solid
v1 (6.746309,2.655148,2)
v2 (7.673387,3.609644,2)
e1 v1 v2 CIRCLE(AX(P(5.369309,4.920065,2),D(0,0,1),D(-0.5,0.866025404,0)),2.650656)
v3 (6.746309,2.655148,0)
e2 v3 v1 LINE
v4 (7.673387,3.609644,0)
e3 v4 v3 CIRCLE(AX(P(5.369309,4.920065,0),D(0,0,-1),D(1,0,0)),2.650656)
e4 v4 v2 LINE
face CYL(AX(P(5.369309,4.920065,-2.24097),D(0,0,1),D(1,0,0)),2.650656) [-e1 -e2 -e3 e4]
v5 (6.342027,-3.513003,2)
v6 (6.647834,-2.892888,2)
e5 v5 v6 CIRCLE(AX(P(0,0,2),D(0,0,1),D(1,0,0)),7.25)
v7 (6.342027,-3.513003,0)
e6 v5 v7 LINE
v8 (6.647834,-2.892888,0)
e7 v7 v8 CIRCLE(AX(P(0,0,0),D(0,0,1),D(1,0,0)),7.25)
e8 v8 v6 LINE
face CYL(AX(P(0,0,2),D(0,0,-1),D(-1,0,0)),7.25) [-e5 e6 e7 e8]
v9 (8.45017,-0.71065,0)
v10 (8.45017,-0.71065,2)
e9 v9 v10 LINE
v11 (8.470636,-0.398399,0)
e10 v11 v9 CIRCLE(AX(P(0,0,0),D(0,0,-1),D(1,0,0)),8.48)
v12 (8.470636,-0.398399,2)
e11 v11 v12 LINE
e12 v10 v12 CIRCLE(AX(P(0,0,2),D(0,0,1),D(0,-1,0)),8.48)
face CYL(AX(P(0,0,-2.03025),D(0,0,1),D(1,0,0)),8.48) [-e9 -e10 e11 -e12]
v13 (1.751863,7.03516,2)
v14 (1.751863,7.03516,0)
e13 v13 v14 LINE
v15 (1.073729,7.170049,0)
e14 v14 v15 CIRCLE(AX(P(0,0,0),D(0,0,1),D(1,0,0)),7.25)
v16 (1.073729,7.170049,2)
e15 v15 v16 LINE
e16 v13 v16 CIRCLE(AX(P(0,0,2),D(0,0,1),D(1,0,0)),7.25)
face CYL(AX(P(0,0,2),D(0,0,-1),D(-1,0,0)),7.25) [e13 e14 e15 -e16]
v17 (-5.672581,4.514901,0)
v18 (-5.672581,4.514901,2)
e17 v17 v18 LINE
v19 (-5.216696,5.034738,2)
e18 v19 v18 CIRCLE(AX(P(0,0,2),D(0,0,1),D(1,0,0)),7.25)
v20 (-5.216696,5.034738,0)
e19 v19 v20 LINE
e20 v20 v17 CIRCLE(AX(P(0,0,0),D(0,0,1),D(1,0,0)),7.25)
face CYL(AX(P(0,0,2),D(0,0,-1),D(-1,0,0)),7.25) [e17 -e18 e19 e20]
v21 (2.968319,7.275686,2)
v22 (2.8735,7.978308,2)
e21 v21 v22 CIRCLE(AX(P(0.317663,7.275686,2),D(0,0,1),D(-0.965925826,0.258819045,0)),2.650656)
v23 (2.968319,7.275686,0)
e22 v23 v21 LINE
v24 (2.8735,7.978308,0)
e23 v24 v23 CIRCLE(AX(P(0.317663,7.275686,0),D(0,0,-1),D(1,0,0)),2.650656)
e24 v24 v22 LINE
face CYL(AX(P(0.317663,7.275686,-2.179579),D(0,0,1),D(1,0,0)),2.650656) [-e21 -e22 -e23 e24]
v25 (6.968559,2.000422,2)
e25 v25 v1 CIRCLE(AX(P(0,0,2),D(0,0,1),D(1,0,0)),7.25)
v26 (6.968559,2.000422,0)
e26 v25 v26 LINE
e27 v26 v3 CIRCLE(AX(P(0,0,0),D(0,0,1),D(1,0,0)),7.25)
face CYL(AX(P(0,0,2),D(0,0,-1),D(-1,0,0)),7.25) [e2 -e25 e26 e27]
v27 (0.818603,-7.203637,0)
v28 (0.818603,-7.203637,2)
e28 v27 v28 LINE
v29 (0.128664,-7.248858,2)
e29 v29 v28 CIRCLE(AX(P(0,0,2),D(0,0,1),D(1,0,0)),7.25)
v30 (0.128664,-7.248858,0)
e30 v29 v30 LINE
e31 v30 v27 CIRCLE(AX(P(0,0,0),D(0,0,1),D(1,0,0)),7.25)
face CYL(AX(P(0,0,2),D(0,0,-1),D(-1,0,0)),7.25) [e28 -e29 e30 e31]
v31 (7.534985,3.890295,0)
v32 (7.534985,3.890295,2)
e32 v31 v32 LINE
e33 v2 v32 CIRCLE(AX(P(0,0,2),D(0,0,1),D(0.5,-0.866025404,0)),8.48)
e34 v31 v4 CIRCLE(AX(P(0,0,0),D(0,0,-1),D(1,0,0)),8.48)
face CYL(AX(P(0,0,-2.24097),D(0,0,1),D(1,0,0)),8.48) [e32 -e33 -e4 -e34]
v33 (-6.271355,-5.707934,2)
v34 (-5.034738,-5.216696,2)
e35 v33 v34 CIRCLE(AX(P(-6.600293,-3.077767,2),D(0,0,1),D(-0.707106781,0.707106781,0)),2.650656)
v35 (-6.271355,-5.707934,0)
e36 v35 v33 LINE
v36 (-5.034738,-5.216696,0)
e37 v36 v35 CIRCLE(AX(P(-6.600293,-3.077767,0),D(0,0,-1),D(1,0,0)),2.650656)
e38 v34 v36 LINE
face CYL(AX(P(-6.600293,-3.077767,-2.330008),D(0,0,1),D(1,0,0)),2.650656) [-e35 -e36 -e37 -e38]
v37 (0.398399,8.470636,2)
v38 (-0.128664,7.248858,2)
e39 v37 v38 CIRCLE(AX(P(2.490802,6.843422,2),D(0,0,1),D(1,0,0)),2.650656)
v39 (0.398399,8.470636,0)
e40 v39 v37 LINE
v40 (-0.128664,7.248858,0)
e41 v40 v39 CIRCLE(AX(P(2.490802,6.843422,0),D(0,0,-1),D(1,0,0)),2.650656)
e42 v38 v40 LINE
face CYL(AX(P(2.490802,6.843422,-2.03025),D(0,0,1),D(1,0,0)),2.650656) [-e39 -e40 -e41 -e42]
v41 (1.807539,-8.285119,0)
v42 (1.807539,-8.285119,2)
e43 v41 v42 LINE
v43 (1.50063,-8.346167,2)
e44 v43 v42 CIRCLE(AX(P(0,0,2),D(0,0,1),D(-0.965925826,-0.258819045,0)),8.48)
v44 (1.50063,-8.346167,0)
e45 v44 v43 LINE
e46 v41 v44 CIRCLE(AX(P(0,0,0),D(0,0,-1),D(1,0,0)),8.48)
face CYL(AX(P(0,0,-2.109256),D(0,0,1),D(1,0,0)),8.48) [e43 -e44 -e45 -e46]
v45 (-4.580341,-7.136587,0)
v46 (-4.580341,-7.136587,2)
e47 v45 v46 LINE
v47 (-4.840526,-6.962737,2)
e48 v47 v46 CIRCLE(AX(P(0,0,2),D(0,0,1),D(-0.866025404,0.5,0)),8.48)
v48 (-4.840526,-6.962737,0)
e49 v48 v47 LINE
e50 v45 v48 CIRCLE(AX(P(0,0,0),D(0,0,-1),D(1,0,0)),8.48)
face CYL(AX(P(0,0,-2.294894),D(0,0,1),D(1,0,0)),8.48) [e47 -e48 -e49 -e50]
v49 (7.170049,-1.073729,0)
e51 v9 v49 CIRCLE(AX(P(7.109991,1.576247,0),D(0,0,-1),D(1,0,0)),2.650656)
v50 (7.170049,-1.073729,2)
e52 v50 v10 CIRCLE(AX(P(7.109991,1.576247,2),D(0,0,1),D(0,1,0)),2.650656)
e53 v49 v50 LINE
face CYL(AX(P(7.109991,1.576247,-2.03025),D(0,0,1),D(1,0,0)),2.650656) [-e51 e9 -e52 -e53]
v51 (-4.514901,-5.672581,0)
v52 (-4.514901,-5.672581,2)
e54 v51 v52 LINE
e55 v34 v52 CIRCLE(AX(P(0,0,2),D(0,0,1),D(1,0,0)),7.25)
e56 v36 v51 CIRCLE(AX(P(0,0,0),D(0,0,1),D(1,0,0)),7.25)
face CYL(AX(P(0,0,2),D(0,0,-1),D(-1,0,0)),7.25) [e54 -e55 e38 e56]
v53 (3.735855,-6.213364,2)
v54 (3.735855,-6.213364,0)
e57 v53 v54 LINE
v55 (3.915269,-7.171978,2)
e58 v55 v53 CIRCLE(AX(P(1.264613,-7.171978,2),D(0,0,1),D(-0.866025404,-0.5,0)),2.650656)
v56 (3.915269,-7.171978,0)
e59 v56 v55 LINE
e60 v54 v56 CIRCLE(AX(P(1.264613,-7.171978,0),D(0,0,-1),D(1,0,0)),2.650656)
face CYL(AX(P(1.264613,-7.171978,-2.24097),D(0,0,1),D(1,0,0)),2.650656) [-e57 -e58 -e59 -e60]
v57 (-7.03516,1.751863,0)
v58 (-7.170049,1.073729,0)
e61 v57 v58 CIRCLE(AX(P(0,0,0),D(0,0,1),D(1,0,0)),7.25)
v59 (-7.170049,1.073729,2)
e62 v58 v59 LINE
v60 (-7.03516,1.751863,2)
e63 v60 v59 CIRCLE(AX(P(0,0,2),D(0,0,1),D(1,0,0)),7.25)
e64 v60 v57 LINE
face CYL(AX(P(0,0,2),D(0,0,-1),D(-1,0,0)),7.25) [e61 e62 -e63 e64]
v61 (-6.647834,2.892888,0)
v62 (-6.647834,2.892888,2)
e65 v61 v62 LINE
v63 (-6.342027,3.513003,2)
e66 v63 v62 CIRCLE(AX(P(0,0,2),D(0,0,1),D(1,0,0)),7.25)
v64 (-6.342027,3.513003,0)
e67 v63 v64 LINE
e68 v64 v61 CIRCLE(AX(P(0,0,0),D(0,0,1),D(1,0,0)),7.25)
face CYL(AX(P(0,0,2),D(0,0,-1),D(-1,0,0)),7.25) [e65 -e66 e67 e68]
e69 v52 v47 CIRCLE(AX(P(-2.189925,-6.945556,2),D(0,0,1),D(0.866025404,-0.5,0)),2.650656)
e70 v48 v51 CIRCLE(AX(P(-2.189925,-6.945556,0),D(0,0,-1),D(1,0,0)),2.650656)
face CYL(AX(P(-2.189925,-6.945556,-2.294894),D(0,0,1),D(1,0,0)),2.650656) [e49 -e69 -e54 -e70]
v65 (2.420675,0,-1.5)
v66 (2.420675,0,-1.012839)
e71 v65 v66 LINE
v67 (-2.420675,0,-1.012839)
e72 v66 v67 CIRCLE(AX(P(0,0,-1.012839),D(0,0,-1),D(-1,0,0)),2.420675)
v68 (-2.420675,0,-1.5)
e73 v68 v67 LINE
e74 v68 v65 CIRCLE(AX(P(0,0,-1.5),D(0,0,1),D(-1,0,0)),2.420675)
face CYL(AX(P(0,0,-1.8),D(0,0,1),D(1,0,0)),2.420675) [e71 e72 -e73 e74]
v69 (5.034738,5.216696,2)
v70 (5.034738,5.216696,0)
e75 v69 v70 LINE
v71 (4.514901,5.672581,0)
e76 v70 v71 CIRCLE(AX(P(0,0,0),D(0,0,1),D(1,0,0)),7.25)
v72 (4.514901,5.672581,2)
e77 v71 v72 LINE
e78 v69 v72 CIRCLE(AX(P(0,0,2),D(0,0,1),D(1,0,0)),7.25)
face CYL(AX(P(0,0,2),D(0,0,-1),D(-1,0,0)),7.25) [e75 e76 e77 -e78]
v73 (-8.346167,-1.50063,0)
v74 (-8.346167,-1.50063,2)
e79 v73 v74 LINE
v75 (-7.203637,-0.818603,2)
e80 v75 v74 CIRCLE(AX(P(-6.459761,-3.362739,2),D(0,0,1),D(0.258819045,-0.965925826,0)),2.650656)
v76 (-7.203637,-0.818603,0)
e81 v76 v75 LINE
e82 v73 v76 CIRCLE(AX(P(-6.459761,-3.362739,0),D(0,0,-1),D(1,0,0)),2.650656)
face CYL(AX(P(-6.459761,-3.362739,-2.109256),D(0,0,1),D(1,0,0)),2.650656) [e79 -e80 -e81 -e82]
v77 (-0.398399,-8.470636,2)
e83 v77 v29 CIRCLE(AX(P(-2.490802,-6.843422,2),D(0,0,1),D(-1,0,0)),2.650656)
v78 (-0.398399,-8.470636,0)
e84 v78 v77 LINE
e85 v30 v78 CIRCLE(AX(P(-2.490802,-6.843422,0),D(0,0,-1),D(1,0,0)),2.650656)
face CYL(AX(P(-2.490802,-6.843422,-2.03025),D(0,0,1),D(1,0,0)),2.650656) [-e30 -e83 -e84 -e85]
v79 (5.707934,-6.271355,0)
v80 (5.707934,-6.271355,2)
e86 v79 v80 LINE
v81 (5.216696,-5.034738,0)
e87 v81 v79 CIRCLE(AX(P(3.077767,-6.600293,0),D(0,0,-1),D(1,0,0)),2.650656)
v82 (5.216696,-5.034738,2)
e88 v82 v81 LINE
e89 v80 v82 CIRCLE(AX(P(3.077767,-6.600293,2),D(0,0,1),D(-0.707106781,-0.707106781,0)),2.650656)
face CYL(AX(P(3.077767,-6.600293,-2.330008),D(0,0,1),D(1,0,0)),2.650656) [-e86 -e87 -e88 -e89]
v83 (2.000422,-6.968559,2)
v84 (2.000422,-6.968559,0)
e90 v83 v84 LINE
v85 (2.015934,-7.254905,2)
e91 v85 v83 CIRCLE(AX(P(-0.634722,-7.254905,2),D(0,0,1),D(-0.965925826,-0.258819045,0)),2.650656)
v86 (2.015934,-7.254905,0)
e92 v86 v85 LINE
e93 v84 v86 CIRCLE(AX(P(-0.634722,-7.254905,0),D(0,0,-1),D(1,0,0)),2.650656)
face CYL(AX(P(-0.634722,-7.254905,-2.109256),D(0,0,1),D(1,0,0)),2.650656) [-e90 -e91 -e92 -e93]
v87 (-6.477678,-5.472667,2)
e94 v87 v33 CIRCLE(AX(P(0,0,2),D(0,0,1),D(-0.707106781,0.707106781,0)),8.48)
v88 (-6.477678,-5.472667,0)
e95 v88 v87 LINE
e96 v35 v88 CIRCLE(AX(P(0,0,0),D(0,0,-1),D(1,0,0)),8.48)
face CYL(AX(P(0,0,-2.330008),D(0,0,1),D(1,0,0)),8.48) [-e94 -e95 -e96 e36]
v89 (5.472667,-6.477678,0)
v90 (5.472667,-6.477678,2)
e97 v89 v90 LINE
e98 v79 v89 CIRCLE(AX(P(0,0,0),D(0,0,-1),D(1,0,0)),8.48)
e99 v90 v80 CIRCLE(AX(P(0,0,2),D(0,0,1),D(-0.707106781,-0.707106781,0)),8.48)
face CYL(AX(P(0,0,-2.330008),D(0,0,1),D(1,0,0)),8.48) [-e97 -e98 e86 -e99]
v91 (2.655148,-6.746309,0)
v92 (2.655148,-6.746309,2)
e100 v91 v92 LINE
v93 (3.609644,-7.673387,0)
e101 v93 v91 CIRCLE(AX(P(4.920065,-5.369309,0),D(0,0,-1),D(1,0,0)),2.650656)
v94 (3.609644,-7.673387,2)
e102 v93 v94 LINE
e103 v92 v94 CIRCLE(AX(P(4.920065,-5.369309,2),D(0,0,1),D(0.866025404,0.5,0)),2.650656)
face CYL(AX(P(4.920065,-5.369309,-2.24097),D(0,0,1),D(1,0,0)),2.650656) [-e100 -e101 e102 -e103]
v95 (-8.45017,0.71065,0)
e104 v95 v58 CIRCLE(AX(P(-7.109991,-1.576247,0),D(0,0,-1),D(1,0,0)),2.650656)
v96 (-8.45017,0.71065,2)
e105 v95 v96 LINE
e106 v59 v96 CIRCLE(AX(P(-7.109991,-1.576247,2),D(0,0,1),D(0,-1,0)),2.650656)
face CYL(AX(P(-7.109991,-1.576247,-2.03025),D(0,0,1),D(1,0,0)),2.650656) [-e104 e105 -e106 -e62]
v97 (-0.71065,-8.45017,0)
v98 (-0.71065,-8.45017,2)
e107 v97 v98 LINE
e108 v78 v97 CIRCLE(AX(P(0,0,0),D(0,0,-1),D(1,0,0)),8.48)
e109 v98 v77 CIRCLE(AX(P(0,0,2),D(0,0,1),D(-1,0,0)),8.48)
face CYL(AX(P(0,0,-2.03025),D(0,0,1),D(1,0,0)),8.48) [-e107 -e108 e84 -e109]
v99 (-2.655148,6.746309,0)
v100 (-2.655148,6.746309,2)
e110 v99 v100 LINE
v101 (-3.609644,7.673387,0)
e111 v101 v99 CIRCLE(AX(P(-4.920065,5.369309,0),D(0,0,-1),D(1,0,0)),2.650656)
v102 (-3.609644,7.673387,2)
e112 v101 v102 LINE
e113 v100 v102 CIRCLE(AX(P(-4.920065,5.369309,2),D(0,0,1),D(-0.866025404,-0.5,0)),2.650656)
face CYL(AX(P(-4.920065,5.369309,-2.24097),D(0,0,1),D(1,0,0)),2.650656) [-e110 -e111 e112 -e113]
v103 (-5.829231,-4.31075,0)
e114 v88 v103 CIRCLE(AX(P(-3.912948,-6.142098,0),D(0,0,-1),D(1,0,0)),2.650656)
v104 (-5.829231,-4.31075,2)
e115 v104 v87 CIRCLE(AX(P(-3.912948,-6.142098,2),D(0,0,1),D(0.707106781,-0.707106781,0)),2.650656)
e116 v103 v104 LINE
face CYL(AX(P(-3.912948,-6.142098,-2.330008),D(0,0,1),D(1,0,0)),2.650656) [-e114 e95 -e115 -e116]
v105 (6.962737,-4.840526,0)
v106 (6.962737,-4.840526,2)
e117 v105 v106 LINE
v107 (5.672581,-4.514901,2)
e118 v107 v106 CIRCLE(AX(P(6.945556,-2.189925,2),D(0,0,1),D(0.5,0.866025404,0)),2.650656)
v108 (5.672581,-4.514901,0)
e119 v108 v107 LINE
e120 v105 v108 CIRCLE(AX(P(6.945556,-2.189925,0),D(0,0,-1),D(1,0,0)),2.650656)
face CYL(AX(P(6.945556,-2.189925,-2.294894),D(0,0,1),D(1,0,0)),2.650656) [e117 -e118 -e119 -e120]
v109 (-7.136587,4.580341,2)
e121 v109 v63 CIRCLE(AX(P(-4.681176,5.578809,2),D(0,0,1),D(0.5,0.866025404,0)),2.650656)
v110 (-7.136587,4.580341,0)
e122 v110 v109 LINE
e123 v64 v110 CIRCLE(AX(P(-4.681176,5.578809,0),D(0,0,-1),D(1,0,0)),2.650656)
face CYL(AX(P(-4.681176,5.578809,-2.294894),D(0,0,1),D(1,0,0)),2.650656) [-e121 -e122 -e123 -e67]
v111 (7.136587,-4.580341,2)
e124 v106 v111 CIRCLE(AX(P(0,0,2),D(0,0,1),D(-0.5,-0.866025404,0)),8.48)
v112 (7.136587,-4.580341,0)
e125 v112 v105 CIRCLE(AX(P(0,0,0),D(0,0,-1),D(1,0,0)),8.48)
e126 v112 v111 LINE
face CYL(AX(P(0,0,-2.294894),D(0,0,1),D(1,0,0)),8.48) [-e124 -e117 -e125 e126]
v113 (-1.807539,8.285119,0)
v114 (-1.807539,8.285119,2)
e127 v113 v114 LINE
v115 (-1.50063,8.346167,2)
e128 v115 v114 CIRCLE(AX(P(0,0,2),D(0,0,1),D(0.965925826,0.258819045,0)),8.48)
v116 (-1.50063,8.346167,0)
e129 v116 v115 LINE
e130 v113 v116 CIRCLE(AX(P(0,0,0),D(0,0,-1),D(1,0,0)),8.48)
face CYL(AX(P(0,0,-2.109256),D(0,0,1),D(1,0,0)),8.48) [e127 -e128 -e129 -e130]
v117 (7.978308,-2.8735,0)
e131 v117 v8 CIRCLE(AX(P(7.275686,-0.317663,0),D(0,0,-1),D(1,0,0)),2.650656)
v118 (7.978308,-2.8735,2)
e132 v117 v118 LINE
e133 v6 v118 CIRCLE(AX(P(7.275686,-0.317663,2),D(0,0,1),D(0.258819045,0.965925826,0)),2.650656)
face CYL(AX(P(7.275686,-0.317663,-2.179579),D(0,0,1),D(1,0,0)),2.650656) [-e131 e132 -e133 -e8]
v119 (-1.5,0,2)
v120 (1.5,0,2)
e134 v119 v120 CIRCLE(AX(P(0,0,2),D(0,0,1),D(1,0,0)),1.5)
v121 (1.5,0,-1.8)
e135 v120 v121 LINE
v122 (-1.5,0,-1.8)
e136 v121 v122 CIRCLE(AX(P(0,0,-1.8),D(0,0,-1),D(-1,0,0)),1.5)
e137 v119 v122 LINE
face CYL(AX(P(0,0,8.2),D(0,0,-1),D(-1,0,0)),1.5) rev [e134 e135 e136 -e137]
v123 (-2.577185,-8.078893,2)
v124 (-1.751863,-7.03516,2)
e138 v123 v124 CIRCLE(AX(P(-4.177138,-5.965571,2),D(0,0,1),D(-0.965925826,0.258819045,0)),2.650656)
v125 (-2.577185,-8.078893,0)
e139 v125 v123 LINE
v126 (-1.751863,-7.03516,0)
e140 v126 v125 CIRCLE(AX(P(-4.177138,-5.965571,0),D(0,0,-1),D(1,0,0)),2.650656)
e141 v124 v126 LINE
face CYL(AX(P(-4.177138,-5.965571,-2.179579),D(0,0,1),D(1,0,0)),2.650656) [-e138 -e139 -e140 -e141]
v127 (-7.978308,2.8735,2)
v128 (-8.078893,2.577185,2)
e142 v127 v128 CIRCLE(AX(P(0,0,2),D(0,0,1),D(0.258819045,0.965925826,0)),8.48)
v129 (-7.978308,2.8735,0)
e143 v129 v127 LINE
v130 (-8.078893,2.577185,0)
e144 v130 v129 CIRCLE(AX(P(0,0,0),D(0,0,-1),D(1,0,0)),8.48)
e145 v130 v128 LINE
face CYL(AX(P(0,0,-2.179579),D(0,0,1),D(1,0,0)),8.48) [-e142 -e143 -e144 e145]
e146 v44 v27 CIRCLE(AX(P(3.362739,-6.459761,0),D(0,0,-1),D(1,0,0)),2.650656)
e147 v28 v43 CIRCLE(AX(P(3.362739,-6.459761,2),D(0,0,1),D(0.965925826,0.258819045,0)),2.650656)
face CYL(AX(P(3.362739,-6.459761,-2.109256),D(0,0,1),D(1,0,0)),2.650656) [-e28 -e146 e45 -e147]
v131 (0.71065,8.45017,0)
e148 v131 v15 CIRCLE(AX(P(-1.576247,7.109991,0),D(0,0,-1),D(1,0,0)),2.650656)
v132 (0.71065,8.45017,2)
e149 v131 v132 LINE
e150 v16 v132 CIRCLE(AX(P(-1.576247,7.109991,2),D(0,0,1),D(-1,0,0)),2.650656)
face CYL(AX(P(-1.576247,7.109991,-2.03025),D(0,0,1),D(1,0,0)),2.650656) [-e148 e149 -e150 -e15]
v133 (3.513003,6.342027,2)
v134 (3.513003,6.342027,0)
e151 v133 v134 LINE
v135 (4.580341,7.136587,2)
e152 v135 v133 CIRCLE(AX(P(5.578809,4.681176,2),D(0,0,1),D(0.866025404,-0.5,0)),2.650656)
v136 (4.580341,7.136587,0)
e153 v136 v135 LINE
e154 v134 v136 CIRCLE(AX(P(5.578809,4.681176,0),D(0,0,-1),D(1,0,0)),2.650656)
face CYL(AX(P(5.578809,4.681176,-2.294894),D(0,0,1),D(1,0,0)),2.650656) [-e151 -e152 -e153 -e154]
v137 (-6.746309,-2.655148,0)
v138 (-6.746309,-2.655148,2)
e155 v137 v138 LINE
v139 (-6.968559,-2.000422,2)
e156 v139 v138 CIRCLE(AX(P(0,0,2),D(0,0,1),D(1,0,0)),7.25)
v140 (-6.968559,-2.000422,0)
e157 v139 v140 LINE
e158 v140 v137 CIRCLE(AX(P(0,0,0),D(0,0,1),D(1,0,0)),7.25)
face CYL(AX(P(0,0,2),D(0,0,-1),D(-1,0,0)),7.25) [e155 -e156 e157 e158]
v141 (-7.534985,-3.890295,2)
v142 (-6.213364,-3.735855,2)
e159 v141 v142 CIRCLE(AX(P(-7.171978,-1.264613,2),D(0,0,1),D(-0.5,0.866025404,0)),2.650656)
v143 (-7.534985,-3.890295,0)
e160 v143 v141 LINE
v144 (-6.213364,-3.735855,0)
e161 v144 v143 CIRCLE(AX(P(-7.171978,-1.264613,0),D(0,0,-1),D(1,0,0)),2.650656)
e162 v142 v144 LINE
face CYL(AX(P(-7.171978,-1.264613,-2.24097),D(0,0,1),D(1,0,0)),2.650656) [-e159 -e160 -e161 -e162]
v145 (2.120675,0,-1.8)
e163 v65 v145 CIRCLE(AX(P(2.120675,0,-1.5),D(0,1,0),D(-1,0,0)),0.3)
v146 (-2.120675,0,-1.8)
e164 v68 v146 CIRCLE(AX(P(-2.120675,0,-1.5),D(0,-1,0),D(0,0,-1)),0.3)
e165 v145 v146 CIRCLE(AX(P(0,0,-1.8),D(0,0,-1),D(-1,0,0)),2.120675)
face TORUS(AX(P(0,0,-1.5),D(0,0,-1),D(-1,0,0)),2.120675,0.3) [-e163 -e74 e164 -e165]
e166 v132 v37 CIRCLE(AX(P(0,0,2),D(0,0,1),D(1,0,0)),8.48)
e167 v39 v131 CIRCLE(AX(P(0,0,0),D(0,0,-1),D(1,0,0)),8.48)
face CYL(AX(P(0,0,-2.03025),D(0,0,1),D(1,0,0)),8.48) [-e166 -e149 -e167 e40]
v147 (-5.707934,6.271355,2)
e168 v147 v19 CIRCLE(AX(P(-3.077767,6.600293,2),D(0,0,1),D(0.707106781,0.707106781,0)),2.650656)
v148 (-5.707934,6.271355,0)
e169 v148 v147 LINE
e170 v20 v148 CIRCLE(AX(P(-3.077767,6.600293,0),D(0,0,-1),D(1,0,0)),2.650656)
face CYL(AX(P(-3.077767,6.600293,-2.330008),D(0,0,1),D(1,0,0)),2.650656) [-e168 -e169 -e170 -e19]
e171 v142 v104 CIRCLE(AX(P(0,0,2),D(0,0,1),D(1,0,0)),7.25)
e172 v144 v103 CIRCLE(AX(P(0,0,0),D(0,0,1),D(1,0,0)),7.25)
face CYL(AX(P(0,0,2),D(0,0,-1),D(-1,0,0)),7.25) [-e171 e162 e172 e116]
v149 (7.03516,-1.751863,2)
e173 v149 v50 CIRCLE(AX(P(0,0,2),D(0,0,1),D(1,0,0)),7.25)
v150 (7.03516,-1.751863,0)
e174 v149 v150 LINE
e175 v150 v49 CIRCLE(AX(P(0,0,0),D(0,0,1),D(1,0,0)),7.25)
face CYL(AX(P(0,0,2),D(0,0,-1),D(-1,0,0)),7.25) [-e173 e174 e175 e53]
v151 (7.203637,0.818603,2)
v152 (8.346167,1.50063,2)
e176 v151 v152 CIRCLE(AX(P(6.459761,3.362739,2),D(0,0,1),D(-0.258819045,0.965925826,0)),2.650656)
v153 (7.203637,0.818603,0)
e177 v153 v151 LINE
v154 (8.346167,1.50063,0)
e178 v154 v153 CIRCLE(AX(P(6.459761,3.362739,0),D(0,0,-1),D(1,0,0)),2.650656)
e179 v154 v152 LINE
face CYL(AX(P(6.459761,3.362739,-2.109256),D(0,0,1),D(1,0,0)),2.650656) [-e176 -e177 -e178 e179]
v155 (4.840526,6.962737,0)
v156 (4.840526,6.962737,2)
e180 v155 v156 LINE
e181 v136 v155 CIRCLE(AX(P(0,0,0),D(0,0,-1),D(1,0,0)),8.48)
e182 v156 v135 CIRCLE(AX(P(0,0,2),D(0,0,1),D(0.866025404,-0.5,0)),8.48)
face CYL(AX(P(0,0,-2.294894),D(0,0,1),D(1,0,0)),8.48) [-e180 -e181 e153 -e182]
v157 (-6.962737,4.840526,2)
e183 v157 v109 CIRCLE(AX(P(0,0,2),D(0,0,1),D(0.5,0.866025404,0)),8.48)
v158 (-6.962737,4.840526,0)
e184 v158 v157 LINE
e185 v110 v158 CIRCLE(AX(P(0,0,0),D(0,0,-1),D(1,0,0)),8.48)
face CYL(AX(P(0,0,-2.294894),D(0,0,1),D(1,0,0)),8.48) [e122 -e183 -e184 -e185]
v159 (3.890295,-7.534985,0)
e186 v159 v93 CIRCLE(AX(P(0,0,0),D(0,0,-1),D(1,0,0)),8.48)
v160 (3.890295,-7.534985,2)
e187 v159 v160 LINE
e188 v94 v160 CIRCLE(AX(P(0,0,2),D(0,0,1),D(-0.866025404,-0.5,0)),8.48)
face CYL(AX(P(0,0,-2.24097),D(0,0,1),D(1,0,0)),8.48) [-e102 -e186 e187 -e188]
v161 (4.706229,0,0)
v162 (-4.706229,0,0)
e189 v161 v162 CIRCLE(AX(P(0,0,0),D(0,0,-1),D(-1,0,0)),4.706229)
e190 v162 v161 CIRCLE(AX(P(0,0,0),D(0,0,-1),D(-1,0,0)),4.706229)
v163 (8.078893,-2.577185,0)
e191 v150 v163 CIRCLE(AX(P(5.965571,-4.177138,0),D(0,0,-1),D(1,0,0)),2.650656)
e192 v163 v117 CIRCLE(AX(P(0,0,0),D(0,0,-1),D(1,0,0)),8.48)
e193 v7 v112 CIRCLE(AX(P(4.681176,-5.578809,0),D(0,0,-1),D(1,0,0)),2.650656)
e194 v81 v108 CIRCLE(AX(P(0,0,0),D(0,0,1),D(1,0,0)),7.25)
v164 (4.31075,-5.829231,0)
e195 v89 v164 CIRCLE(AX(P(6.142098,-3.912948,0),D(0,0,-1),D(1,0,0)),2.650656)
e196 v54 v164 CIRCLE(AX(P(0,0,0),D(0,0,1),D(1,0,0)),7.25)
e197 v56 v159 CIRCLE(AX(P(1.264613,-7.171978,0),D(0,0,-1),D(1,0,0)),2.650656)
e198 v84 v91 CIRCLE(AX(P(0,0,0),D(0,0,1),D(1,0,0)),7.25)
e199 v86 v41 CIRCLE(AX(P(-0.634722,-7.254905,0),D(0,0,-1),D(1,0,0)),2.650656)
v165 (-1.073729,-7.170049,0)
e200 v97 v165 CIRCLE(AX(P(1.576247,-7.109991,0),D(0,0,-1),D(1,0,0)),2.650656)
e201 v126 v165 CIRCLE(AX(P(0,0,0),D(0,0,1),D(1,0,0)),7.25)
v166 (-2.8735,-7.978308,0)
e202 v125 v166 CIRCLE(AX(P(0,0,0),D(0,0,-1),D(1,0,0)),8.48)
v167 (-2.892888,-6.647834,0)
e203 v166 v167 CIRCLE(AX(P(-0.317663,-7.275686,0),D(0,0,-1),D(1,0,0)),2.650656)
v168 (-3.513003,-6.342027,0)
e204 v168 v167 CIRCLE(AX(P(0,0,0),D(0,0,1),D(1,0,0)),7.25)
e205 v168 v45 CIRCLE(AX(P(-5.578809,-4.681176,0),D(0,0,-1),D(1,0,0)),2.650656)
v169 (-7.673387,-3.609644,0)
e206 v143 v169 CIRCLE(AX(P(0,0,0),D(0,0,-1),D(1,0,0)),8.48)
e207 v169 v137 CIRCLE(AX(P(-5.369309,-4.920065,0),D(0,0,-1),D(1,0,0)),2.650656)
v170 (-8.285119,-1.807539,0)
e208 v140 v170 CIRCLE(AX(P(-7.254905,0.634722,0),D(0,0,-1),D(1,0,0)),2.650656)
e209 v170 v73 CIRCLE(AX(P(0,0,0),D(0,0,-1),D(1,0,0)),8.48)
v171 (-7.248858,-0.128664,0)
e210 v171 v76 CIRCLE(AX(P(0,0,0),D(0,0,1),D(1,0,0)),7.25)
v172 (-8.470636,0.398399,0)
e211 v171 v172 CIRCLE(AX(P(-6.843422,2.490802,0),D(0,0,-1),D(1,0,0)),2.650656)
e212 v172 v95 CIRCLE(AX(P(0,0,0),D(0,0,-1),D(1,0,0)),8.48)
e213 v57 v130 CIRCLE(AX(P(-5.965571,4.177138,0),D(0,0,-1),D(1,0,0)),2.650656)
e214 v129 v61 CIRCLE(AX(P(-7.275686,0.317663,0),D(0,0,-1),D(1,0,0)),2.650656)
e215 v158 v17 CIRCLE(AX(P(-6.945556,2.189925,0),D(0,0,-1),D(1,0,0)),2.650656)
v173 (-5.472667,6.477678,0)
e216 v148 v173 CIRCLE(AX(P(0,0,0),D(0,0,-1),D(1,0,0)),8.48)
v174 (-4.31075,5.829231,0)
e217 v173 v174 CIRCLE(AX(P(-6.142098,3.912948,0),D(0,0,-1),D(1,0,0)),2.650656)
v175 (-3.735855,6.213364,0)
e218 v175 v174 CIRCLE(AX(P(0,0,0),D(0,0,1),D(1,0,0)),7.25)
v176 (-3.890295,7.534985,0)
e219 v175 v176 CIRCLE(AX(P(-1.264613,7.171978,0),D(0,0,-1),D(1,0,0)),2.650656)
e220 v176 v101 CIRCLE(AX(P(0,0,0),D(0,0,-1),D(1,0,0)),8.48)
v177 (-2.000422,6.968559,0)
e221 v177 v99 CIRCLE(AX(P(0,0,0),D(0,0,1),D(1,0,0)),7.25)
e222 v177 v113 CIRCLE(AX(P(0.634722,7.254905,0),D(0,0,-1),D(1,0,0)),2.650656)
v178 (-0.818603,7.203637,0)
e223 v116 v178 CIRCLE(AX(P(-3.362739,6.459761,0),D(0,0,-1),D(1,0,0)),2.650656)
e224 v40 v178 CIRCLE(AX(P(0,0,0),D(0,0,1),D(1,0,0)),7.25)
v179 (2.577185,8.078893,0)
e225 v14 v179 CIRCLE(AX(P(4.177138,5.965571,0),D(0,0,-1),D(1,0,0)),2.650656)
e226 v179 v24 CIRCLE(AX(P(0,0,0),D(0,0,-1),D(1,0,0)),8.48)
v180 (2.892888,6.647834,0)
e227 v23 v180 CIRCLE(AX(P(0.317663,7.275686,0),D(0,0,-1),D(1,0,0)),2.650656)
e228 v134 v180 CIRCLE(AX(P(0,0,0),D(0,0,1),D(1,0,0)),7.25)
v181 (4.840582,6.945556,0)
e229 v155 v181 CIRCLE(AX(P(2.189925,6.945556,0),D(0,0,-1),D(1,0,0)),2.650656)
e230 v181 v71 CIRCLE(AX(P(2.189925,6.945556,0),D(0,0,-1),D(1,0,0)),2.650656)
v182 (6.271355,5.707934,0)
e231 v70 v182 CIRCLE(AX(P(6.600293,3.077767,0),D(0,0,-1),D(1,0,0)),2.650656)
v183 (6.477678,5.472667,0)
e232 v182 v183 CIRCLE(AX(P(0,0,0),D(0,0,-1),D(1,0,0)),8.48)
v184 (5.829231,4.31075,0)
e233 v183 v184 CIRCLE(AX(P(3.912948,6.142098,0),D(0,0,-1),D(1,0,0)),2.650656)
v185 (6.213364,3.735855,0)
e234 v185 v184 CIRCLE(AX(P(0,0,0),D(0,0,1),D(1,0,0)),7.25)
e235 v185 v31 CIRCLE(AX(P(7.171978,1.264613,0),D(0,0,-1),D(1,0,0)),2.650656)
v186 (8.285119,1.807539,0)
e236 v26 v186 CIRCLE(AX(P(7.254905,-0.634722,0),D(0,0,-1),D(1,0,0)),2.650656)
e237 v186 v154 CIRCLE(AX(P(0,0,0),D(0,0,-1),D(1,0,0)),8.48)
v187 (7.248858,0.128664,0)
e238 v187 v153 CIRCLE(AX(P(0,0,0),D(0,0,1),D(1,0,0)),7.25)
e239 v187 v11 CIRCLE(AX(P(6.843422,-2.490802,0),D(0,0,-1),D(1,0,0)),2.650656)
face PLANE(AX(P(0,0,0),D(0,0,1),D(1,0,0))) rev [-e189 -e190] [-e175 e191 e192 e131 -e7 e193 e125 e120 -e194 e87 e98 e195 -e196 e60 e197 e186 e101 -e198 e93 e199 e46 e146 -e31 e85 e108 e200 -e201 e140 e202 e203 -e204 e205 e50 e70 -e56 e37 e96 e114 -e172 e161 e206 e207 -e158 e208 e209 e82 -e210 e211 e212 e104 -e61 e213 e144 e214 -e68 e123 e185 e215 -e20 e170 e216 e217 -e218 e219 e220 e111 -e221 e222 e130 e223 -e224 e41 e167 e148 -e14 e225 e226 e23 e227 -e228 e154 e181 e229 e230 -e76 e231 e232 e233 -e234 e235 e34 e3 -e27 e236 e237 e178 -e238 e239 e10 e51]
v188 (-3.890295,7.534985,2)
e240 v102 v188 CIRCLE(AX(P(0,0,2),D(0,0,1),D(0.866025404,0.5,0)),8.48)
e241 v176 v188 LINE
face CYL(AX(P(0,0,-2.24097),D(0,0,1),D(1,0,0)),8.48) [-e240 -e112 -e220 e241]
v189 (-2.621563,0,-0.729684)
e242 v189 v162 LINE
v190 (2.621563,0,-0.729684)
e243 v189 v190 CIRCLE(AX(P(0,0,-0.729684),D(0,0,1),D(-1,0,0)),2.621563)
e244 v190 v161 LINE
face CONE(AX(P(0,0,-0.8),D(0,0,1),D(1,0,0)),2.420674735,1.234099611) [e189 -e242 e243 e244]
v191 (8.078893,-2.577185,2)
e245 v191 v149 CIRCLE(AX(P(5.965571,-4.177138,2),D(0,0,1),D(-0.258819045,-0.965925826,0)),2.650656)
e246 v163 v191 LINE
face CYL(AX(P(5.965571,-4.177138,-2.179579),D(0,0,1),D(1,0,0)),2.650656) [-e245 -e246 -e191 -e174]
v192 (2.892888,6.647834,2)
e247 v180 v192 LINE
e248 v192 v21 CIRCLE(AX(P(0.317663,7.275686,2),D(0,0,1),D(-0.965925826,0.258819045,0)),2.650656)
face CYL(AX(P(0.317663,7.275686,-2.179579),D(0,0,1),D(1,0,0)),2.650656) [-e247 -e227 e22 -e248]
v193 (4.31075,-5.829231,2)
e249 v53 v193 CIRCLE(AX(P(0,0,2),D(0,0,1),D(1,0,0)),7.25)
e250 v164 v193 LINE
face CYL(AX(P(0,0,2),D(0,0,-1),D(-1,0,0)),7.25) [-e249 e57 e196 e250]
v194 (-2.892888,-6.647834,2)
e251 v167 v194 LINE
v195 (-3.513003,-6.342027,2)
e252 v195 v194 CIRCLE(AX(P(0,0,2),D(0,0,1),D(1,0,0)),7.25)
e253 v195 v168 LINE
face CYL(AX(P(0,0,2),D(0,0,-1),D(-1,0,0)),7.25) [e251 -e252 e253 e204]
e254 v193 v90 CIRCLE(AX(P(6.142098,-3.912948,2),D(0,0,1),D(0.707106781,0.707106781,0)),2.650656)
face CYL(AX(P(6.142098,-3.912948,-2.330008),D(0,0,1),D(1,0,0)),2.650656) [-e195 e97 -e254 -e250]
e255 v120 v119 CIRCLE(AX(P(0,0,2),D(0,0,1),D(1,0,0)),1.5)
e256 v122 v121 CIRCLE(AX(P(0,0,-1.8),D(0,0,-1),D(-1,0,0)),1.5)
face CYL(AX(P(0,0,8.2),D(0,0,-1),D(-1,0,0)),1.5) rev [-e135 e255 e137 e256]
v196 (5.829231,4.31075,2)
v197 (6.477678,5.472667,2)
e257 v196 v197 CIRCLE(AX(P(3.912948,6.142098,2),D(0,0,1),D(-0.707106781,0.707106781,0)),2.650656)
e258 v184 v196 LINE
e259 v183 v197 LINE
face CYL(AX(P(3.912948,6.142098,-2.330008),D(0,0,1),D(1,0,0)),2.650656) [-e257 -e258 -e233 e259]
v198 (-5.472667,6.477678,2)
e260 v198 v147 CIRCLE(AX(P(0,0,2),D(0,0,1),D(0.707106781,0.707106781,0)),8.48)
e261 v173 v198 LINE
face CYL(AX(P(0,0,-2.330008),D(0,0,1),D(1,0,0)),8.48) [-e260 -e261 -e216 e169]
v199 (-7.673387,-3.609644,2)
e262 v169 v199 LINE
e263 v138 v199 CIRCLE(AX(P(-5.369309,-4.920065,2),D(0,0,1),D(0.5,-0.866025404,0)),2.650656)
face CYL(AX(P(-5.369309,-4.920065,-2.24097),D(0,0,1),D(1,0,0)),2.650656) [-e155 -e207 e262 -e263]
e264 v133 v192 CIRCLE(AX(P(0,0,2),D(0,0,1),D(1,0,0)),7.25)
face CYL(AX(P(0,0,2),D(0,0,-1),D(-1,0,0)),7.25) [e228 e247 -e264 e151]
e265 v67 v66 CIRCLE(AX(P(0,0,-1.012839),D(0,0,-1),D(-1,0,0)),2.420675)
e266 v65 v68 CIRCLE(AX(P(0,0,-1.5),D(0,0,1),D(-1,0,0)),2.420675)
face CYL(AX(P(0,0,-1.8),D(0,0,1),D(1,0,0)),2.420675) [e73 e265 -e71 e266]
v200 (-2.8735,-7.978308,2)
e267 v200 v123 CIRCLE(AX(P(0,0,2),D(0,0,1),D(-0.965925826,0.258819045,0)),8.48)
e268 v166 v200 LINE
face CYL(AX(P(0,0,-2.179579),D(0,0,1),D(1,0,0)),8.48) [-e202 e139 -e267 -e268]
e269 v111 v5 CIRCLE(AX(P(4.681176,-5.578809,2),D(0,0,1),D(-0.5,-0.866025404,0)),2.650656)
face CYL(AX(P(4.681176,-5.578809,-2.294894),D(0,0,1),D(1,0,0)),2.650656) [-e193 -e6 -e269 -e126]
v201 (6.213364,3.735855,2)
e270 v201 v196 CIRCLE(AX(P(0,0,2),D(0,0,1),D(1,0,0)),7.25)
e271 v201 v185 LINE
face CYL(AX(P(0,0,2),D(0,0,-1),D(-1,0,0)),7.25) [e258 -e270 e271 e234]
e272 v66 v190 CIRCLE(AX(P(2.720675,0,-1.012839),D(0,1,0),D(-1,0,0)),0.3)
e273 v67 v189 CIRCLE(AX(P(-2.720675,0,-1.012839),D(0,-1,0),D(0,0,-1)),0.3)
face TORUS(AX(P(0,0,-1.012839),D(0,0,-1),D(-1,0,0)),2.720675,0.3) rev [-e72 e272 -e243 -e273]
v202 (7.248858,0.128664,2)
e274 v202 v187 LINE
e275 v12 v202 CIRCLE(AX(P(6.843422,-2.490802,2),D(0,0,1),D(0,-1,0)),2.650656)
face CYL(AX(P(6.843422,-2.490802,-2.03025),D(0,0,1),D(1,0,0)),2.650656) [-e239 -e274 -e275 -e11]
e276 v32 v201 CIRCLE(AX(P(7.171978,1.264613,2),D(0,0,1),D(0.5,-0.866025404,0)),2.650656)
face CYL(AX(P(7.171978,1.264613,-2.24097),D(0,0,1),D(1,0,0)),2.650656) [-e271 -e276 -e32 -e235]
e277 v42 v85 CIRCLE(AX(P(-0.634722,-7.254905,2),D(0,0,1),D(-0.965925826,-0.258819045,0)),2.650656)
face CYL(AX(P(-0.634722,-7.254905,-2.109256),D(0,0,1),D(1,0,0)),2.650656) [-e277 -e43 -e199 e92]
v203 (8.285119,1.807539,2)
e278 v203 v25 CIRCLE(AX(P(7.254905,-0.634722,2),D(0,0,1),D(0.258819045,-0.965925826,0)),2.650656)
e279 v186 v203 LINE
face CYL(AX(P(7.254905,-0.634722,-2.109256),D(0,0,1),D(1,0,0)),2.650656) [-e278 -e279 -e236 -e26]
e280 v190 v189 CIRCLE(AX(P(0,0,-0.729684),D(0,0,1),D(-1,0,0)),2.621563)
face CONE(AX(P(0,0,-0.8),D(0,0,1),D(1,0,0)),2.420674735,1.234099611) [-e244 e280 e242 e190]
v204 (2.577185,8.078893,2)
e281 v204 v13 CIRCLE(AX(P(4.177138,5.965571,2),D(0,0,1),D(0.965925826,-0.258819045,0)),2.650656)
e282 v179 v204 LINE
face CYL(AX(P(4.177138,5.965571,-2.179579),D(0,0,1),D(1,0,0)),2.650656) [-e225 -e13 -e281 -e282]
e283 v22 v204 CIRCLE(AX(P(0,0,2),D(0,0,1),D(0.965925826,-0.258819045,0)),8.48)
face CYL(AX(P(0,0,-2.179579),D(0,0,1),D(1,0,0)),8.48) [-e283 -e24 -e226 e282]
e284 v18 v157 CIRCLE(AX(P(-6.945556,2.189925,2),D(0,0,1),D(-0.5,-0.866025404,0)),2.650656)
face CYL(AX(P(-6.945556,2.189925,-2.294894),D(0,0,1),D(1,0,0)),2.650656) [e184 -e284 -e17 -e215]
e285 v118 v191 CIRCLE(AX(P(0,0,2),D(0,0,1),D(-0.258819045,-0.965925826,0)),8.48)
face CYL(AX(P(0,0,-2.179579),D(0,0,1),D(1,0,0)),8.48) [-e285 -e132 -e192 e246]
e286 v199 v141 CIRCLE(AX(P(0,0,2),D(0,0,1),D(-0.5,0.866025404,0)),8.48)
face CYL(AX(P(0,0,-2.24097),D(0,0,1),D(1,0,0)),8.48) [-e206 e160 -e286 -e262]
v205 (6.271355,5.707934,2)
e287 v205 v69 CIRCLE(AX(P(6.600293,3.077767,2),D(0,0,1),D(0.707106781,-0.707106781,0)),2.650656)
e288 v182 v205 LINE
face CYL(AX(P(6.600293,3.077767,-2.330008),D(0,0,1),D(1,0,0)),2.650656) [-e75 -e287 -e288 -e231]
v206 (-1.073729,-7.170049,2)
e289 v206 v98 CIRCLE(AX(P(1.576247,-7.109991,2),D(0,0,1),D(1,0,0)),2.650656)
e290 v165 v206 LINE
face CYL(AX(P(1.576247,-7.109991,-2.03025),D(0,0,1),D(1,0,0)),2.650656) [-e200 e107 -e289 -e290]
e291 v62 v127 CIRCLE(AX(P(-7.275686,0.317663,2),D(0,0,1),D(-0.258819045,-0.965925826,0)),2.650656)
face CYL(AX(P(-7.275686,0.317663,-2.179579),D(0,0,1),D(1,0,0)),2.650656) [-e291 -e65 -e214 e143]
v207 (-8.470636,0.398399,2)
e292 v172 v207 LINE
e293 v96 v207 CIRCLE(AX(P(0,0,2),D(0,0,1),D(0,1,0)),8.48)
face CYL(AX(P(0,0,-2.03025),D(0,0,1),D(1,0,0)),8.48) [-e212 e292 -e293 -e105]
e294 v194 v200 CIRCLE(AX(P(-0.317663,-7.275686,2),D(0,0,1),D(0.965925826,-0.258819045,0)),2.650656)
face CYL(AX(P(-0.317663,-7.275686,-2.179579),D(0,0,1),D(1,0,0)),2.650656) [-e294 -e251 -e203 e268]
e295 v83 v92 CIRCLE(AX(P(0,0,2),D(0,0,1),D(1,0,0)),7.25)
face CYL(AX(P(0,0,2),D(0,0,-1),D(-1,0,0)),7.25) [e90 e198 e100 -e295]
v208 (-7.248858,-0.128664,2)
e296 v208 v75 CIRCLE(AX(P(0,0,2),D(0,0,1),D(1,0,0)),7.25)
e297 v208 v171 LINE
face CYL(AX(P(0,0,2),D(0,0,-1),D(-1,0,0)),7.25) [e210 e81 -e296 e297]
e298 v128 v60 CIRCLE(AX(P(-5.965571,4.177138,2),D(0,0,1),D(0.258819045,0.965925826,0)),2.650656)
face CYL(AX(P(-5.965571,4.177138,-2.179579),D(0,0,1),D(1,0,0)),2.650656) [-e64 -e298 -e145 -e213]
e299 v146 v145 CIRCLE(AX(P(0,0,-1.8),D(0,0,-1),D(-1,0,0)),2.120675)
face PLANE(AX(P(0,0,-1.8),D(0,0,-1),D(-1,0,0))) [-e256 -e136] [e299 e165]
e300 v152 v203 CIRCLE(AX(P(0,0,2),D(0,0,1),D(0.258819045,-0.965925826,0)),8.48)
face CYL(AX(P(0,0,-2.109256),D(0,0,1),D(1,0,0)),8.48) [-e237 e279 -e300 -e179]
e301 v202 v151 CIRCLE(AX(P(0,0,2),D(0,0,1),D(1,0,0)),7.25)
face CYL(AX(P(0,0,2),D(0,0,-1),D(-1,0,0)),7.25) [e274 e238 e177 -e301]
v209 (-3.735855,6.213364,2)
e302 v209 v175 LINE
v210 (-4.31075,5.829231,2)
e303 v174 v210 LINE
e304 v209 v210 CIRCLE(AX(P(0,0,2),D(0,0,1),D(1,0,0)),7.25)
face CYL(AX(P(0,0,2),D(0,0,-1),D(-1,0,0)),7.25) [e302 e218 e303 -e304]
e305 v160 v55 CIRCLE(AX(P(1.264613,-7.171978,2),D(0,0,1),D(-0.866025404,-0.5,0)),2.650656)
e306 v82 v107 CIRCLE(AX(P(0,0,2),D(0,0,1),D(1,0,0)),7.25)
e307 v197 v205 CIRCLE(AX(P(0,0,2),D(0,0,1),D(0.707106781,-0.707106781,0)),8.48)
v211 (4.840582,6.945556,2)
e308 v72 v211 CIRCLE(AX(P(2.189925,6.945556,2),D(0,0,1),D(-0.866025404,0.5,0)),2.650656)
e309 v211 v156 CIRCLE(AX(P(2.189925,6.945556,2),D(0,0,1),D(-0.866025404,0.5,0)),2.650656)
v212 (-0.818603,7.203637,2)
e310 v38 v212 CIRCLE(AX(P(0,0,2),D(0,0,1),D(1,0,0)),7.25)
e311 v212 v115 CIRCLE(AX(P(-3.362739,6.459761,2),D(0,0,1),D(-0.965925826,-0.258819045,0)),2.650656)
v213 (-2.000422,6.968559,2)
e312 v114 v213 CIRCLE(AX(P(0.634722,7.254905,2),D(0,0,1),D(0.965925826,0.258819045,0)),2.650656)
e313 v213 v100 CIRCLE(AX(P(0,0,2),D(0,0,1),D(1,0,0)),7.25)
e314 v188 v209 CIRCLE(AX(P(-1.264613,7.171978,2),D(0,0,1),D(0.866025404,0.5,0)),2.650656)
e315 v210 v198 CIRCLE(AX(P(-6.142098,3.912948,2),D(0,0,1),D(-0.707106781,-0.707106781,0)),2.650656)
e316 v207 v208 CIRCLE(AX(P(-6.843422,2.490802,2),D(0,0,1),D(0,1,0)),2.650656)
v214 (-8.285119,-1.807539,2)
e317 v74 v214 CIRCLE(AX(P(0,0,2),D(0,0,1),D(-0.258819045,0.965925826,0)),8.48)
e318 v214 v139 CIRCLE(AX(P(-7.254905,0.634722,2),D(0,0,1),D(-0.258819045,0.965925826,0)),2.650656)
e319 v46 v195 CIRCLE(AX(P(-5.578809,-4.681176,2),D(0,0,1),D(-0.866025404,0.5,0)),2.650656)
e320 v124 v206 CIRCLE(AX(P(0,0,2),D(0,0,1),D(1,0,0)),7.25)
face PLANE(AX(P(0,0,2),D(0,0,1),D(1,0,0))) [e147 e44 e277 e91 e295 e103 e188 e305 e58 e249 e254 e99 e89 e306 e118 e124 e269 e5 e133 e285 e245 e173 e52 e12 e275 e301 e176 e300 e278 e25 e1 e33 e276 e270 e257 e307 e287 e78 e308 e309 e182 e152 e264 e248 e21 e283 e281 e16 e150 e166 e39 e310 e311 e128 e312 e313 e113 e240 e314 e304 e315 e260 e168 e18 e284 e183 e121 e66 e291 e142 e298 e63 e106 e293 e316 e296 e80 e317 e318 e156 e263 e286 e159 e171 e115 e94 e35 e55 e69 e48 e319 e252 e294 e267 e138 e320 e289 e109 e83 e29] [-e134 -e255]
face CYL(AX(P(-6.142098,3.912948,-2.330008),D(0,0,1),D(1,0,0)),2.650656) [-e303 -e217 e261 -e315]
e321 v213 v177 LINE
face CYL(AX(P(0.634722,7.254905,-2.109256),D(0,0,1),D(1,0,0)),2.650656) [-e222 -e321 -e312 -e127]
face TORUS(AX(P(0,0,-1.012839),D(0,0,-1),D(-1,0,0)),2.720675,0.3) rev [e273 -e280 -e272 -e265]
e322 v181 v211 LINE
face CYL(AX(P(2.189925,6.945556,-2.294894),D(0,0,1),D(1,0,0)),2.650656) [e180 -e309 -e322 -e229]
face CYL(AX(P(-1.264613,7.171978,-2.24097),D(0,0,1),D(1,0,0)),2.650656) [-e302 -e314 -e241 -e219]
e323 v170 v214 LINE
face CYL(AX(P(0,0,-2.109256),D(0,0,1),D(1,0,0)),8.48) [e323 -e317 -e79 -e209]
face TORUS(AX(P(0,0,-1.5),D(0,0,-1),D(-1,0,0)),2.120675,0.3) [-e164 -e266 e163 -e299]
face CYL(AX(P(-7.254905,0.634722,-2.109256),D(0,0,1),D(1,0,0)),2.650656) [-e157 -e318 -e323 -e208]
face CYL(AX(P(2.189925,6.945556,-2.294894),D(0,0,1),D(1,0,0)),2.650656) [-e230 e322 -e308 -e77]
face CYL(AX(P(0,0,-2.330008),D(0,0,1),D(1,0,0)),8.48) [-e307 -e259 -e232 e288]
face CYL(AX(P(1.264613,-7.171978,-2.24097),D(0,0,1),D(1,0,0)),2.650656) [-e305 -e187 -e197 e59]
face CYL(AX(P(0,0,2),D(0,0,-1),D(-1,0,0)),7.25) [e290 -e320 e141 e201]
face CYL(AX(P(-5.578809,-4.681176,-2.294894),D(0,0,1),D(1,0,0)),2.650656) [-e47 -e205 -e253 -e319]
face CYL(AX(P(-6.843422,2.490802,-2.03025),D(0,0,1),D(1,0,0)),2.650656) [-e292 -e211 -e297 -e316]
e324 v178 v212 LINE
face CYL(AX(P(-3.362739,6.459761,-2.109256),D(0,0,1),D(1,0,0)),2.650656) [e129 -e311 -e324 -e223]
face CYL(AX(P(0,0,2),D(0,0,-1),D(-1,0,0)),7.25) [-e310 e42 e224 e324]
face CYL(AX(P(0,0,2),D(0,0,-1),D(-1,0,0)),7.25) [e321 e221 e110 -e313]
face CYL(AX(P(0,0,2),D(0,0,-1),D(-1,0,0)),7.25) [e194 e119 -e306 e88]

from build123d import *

# Parameters (mm, degrees)
SKETCH1_R           = 7.25
BOSS_EXTRUDE1_DEPTH = 2
SKETCH3_R           = 4.70622852
SKETCH4_R           = 2.420674735
SKETCH5_R           = 2.420674735
BOSS_EXTRUDE3_DEPTH = 1
FILLET1_R           = 0.3
BOSS_EXTRUDE4_DEPTH = 2
CIRPATTERN2_COUNT   = 24
SKETCH6_R           = 1.5
CUT_EXTRUDE1_DEPTH  = 10


with BuildPart() as part:
    # Sketch1 → Boss-Extrude1 (new body)
    with BuildSketch(Plane.XY):
        Circle(SKETCH1_R)
    extrude(amount=BOSS_EXTRUDE1_DEPTH)

    # Sketch3 → Loft1 section 0
    with BuildSketch(Plane(origin=(0, 0, 0), x_dir=(-1, 0, 0), z_dir=(0, 0, -1))):
        Circle(SKETCH3_R)
    # Sketch4 → Loft1 section 1
    with BuildSketch(Plane(origin=(0, 0, -0.8), x_dir=(-1, 0, 0), z_dir=(0, 0, -1))):
        Circle(SKETCH4_R)
    loft()

    # Sketch5 → Boss-Extrude3 (add)
    with BuildSketch(Plane(origin=(0, 0, -0.8), x_dir=(-1, 0, 0), z_dir=(0, 0, -1))):
        Circle(SKETCH5_R)
    extrude(amount=BOSS_EXTRUDE3_DEPTH)

    # Fillet1
    fillet1_edges = [part.edges().sort_by_distance(p)[0] for p in [
        (2.420674735, 0, -1.8),
        (2.420674735, 0, -0.8),
    ]]
    fillet(fillet1_edges, radius=FILLET1_R)

    # Sketch2 → Boss-Extrude4 (add)
    with BuildSketch(Plane.XY.offset(2)):
        with BuildLine():
            ThreePointArc((0.710649734, 8.450170232), (0.554618536, 8.461843669), (0.398398517, 8.470636258))
            ThreePointArc((0.398398517, 8.470636258), (-0.000769738, 7.747882363), (-0.158188639, 6.937371549))
            ThreePointArc((-0.158188639, 6.937371549), (0.45384375, 6.924317548), (1.062344006, 6.857373613))
            ThreePointArc((1.062344006, 6.857373613), (1.012064735, 7.681497684), (0.710649734, 8.450170232))
        make_face()
    boss_extrude4 = extrude(amount=-BOSS_EXTRUDE4_DEPTH)

    # CirPattern2: Boss-Extrude4 ×24 about axis
    cirpattern2_axis = Axis((0, 0, 0), (0, 0, 1))
    for i in range(1, CIRPATTERN2_COUNT):
        add(boss_extrude4.rotate(cirpattern2_axis, i * 360 / CIRPATTERN2_COUNT))

    # Sketch6 → Cut-Extrude1 (cut)
    with BuildSketch(Plane(origin=(0, 0, -1.8), x_dir=(-1, 0, 0), z_dir=(0, 0, -1))):
        Circle(SKETCH6_R)
    extrude(amount=-CUT_EXTRUDE1_DEPTH, mode=Mode.SUBTRACT)


solid = part.part
